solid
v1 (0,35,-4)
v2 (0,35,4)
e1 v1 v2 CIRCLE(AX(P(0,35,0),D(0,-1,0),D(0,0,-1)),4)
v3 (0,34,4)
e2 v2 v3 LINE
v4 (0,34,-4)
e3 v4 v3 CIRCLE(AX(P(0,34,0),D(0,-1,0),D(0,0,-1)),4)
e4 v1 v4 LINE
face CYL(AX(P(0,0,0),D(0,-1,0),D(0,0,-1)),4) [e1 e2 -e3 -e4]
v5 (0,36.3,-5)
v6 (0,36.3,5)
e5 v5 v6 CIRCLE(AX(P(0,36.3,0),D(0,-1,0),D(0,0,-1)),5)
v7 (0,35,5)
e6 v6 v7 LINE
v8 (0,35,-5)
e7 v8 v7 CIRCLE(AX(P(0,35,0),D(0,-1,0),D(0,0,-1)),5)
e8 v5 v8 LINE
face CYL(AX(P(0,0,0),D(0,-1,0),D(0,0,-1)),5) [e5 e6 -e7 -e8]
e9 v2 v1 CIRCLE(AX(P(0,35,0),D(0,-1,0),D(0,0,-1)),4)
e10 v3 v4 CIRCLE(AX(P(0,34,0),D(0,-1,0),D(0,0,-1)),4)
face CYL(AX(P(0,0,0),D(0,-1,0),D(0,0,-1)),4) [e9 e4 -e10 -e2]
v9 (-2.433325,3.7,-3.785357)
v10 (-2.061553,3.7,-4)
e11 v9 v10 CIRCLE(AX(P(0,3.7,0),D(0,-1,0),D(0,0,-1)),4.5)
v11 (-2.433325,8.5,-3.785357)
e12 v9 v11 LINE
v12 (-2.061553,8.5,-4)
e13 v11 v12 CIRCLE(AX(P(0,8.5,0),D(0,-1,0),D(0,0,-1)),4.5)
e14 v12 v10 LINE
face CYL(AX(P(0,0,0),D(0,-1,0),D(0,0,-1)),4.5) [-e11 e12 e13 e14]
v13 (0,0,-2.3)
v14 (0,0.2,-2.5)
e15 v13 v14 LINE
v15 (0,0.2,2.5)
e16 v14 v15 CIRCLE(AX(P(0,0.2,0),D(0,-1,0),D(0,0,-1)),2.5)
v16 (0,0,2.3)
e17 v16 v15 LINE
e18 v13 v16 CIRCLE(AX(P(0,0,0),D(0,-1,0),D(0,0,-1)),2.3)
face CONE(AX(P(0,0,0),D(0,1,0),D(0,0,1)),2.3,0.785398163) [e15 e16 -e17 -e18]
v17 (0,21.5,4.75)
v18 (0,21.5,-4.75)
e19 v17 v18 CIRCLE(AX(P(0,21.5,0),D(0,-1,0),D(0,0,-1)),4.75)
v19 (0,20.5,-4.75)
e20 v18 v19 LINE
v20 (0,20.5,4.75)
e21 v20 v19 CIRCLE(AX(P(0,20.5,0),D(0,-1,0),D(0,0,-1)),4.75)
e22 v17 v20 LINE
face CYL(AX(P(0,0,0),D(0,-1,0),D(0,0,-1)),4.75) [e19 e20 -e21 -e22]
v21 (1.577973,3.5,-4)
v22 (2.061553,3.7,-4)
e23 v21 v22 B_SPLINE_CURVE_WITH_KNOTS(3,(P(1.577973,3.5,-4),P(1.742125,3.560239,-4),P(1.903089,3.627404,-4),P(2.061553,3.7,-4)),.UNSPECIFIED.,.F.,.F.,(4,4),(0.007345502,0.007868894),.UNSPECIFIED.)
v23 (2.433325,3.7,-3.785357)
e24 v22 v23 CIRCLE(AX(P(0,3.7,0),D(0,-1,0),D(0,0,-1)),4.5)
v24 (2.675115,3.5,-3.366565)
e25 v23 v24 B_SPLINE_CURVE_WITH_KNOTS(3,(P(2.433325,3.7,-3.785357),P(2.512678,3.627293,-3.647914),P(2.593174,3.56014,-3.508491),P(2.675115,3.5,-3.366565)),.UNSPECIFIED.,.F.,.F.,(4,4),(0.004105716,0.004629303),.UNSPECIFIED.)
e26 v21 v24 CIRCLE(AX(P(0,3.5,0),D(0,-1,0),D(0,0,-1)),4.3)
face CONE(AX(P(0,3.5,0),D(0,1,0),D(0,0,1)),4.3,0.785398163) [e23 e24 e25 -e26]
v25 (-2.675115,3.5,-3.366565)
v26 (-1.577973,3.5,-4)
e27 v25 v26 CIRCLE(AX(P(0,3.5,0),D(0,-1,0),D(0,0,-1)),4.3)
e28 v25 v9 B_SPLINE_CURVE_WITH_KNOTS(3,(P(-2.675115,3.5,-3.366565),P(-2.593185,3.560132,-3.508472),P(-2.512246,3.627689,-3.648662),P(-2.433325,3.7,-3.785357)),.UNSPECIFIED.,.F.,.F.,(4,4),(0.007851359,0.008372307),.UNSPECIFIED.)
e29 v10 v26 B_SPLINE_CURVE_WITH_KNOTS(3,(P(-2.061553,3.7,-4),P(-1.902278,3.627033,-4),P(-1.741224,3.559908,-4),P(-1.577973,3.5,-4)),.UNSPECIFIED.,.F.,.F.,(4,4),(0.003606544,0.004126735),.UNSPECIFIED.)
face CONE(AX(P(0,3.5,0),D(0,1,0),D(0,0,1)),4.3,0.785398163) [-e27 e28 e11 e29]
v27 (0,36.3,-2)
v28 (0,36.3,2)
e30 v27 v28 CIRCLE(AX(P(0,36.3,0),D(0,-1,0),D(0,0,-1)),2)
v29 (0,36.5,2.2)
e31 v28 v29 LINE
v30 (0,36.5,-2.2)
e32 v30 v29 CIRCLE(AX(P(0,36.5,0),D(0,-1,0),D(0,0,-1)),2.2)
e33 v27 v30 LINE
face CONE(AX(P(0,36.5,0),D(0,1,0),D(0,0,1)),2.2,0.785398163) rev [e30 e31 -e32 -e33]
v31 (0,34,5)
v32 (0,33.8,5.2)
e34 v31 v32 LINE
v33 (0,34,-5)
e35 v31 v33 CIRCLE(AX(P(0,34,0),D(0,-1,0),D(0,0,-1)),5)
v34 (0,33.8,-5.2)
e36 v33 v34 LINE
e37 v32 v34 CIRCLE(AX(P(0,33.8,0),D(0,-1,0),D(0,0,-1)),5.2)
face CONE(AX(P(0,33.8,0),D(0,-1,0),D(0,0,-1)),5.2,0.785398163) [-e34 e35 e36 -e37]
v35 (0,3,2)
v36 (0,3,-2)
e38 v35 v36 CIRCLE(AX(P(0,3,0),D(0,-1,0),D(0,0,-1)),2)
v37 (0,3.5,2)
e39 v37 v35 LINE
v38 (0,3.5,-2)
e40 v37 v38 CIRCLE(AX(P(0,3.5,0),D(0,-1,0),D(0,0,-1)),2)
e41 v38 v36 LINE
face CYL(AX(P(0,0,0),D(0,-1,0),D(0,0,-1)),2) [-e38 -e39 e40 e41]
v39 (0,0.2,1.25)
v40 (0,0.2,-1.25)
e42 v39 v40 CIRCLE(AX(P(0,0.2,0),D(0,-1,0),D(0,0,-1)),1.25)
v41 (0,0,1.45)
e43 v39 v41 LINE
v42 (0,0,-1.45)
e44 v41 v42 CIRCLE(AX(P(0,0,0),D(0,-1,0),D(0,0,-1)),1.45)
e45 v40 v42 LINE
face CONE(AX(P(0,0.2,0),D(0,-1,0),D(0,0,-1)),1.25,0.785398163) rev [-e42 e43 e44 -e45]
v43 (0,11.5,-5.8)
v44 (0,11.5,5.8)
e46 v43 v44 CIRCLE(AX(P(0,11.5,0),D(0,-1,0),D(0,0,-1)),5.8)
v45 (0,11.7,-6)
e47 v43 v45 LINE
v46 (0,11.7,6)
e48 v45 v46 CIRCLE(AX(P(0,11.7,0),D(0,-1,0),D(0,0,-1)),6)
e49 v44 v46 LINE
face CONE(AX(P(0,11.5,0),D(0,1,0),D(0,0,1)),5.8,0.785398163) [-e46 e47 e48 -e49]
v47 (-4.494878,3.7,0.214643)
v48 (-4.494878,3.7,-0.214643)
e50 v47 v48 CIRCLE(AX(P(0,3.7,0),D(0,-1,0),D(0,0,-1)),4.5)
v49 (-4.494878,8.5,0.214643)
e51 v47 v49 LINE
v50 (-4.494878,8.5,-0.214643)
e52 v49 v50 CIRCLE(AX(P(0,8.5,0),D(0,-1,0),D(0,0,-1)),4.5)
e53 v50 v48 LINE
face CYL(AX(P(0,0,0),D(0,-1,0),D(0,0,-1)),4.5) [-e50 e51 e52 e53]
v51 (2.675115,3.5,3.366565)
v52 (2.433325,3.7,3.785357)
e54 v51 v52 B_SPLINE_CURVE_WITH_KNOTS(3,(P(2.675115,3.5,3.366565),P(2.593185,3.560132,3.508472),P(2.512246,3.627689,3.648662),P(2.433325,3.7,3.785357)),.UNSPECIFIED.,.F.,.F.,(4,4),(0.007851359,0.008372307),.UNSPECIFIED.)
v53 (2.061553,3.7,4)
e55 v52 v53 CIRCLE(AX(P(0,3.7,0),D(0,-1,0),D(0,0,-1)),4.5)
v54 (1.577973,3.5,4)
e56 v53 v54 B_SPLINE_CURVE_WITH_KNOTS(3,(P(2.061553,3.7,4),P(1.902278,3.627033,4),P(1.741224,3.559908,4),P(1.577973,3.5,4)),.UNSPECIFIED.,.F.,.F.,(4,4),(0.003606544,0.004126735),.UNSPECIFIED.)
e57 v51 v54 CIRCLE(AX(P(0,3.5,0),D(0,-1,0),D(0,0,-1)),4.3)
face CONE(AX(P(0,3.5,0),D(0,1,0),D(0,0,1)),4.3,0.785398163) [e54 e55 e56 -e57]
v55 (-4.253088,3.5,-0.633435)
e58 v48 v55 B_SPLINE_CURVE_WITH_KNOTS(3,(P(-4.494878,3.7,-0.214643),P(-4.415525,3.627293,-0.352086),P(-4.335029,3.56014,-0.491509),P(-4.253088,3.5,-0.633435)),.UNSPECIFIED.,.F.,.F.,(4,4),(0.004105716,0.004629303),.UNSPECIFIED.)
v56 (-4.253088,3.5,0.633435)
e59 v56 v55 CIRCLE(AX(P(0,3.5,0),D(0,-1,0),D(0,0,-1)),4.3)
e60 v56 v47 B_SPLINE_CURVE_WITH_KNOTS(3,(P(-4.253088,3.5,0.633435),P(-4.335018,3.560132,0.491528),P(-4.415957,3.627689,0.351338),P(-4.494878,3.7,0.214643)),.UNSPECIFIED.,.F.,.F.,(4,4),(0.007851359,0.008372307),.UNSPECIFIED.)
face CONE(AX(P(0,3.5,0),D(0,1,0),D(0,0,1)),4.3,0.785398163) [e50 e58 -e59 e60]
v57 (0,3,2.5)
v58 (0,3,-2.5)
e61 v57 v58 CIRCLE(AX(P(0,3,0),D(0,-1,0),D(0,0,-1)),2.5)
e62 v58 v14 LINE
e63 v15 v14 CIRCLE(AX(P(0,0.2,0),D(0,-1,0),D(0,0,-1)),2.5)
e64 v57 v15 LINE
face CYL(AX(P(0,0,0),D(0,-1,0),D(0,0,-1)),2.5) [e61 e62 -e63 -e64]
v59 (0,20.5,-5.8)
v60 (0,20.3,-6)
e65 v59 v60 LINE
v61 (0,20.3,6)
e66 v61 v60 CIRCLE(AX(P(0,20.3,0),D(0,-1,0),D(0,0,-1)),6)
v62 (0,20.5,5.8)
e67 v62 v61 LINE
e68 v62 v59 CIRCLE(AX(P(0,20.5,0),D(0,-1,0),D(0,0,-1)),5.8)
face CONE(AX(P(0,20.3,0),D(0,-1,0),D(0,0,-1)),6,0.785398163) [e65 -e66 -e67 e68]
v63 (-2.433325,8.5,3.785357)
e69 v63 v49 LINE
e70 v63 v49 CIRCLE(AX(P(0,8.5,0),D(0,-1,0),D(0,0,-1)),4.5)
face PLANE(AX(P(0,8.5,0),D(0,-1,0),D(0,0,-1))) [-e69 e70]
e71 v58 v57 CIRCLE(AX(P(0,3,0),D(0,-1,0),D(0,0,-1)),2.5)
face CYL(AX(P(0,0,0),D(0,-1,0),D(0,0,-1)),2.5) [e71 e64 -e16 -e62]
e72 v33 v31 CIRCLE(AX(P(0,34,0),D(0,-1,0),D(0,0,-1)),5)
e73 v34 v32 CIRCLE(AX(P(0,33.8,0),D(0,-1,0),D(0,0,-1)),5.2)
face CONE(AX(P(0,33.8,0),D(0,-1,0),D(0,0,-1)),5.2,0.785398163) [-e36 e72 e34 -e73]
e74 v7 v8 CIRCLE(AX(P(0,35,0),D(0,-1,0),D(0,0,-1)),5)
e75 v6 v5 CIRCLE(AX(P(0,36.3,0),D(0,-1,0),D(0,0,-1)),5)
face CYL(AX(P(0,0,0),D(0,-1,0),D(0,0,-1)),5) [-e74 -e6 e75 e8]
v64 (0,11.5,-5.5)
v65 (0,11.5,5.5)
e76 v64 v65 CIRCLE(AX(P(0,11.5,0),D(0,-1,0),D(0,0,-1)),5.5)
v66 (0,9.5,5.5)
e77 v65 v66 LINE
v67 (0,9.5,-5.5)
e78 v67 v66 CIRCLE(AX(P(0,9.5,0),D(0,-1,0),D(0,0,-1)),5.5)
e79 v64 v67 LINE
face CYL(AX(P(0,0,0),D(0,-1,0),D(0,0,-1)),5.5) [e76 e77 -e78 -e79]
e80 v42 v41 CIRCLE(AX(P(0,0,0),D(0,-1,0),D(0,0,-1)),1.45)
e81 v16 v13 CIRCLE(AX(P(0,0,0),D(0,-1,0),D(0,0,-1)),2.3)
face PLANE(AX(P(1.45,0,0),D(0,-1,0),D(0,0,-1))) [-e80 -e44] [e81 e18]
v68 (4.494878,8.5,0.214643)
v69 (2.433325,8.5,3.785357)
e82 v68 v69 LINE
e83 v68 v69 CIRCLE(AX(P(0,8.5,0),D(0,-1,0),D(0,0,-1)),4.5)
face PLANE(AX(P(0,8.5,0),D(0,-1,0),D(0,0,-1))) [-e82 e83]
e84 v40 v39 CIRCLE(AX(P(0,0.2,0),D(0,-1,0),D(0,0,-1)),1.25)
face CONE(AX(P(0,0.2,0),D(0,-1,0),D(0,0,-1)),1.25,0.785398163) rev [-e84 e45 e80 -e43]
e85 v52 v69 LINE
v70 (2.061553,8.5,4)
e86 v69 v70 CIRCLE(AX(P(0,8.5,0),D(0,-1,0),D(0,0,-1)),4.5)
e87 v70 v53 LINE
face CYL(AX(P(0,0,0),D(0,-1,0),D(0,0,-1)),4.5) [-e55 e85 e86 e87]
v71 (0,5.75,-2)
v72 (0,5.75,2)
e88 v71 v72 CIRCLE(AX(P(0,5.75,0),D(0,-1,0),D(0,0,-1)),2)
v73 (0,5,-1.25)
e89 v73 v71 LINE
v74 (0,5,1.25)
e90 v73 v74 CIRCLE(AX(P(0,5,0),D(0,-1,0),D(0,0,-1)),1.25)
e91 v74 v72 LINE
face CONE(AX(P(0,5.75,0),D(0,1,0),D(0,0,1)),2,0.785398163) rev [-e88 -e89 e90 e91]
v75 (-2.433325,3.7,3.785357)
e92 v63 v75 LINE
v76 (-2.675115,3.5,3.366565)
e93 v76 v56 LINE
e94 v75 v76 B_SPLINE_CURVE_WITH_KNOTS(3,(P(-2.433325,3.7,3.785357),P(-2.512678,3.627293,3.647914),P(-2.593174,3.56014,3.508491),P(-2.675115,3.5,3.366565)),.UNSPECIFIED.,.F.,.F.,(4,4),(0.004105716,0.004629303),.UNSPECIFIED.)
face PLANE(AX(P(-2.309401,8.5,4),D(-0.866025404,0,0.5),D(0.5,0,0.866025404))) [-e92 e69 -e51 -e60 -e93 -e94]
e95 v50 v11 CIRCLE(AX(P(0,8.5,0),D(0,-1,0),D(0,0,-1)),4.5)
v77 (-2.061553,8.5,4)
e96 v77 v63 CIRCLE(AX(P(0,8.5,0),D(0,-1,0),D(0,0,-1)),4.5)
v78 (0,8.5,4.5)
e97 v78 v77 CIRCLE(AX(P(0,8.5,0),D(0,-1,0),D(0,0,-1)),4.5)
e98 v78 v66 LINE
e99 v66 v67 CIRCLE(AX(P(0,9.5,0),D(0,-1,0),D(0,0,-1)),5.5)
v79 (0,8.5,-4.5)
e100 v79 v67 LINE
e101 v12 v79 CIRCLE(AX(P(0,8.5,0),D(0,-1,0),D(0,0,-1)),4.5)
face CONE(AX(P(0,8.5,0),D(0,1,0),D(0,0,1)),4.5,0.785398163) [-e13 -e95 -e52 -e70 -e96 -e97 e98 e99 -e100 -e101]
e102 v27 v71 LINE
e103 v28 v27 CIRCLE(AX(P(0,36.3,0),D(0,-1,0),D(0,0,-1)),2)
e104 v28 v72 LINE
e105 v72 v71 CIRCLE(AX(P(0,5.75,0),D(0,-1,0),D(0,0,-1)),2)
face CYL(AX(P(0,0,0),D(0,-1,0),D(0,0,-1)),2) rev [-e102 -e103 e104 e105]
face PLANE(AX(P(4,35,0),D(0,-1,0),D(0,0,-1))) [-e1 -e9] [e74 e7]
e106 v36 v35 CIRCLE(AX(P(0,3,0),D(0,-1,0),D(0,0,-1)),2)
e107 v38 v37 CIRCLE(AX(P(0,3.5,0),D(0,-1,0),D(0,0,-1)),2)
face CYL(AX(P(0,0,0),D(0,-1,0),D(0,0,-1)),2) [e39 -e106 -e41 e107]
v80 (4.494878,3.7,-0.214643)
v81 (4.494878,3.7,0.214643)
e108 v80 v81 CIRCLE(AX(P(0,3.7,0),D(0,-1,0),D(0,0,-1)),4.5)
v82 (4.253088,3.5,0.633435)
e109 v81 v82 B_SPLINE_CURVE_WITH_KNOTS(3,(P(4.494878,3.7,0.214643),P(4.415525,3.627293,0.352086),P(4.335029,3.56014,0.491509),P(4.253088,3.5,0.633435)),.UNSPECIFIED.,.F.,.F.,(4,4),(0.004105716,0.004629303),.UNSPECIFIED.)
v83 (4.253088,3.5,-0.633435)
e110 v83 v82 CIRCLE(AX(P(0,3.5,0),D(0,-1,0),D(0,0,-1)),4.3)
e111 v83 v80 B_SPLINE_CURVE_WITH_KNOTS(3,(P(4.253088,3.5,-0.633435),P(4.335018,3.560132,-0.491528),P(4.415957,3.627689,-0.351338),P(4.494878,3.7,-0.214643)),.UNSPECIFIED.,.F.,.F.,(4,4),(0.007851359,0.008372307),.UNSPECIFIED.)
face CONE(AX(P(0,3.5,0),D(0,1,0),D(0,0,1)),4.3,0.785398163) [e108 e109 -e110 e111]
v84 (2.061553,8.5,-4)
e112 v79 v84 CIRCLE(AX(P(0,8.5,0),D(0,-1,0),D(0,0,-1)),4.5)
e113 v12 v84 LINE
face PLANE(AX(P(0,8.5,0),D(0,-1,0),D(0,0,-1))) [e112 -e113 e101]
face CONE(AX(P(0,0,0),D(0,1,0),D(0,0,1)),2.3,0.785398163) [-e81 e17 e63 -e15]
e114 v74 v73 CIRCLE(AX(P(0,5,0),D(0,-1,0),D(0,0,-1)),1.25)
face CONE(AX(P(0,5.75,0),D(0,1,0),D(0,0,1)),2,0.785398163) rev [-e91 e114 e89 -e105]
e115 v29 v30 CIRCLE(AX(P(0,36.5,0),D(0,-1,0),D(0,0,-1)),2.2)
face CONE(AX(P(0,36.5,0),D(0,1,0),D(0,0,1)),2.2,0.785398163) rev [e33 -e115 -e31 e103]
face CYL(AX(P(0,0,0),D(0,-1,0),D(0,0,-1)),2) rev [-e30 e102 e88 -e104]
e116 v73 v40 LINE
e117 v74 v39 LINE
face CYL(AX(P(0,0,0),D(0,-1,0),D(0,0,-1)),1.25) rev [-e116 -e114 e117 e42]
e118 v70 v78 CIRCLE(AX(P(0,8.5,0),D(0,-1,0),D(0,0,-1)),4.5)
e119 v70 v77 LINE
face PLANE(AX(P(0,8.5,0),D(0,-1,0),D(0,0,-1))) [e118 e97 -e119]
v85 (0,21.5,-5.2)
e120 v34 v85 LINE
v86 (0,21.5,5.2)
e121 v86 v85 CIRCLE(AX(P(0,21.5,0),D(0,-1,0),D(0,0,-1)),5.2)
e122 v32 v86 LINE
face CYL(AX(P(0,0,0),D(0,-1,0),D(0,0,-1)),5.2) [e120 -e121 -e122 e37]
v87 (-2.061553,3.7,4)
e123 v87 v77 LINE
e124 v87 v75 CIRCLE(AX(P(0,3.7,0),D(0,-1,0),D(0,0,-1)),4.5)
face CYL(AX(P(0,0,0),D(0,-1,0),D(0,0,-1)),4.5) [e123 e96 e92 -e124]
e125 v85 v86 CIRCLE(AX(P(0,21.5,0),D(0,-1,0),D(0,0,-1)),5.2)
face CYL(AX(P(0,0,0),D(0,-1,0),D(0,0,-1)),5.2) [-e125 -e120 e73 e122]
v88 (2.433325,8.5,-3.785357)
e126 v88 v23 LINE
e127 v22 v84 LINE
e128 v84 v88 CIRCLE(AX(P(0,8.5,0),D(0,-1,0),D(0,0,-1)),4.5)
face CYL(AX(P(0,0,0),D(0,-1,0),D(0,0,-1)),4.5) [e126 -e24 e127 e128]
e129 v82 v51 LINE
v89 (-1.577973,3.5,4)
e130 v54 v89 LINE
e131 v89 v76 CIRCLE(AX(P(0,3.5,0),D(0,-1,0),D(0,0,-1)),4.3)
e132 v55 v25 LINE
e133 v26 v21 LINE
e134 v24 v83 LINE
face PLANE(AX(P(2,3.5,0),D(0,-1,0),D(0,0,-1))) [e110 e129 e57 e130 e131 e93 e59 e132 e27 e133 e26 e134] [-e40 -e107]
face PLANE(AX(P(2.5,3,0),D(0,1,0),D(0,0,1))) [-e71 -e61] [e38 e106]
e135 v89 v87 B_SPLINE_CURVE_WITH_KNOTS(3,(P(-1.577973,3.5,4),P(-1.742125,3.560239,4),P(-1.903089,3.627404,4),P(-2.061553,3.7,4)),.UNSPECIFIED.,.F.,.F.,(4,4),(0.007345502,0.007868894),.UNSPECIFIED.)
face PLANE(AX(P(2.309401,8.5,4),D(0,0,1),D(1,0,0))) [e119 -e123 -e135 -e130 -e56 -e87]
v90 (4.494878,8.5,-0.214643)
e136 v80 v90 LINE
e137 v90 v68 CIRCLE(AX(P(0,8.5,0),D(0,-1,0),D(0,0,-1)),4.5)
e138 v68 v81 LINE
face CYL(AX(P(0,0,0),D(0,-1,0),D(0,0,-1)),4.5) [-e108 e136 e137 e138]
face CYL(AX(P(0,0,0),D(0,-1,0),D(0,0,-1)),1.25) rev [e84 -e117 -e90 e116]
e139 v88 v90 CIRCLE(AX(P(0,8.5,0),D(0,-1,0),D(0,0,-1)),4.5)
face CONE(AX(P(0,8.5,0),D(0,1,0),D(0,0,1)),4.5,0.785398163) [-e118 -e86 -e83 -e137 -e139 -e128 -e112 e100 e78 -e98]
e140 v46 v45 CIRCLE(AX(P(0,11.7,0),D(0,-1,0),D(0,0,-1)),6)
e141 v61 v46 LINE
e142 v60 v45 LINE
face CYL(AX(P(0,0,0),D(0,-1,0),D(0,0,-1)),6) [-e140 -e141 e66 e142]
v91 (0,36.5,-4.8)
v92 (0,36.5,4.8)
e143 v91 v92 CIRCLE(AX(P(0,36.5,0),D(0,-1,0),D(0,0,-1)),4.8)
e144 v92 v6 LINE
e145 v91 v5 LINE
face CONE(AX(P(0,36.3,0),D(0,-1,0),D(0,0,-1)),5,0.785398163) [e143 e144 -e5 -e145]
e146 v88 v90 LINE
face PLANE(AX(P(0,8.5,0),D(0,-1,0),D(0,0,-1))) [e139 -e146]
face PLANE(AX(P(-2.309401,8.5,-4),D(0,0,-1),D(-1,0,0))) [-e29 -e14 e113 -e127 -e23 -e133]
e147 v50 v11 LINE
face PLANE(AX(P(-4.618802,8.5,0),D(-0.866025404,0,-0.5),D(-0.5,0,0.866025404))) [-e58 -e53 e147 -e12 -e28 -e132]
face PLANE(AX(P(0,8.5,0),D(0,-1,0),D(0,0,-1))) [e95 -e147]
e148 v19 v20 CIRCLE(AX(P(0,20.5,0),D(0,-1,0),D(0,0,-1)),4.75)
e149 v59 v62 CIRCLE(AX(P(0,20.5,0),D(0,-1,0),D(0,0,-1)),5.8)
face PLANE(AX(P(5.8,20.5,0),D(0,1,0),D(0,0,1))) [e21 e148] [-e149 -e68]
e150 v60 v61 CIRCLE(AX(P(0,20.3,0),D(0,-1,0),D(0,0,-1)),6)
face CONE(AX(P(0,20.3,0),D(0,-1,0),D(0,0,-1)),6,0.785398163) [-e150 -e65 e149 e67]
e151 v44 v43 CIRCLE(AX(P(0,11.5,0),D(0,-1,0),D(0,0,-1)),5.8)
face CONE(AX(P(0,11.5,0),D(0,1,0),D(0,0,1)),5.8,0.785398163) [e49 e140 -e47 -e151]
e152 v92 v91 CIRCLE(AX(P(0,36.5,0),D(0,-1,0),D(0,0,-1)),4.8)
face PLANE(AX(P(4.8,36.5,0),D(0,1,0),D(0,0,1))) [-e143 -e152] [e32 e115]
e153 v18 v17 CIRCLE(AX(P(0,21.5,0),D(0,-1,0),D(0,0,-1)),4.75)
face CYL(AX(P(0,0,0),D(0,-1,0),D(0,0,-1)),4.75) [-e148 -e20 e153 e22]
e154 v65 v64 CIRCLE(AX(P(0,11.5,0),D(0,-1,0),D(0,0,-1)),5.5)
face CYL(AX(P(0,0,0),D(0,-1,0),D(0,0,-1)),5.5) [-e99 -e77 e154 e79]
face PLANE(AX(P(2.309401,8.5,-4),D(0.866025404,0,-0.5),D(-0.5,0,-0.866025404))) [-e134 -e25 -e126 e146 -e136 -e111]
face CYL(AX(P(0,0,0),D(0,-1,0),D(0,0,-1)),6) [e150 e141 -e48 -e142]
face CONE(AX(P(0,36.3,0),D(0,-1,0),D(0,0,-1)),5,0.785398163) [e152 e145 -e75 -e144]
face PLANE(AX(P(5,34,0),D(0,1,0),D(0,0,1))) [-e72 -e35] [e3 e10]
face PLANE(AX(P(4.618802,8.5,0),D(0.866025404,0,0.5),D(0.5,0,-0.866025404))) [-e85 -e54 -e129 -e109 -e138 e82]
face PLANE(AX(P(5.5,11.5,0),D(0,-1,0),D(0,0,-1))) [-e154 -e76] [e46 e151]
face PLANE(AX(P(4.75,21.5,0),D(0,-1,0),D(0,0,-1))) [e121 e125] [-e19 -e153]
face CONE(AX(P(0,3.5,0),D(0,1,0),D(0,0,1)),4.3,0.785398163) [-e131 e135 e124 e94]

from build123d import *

# Parameters (mm, degrees)
SKETCH3_OUTSIDE_W  = 22.05
SKETCH3_OUTSIDE_H  = 22.05
CUT_EXTRUDE1_DEPTH = 5


with BuildPart() as part:
    # Sketch1 → Revolve1 (revolve)
    with BuildSketch(Plane.XY, mode=Mode.PRIVATE) as revolve1_sk:
        Polygon((1.45, 0), (2.3, 0), (2.5, 0.2), (2.5, 3), (2, 3), (2, 3.5), (4.3, 3.5), (4.5, 3.7), (4.5, 8.5), (5.5, 9.5), (5.5, 11.5), (5.8, 11.5), (6, 11.7), (6, 20.3), (5.8, 20.5), (4.75, 20.5), (4.75, 21.5), (5.2, 21.5), (5.2, 33.8), (5, 34), (4, 34), (4, 35), (5, 35), (5, 36.3), (4.8, 36.5), (2.2, 36.5), (2, 36.3), (2, 5.75), (1.25, 5), (1.25, 0.2), align=None)
    revolve(revolve1_sk.sketch.rotate(Axis((0, 0, 0), (0, 1, 0)), 90), axis=Axis((0, 0, 0), (0, 1, 0)))

    # Sketch3 outside → Cut-Extrude1 (cut)
    with BuildSketch(Plane.XZ.offset(-3.5)):
        Rectangle(SKETCH3_OUTSIDE_W, SKETCH3_OUTSIDE_H)
        Polygon((2.309401077, -4), (4.618802154, 0), (2.309401077, 4), (-2.309401077, 4), (-4.618802154, 0), (-2.309401077, -4), align=None, mode=Mode.SUBTRACT)
    extrude(amount=-CUT_EXTRUDE1_DEPTH, mode=Mode.SUBTRACT)


solid = part.part
